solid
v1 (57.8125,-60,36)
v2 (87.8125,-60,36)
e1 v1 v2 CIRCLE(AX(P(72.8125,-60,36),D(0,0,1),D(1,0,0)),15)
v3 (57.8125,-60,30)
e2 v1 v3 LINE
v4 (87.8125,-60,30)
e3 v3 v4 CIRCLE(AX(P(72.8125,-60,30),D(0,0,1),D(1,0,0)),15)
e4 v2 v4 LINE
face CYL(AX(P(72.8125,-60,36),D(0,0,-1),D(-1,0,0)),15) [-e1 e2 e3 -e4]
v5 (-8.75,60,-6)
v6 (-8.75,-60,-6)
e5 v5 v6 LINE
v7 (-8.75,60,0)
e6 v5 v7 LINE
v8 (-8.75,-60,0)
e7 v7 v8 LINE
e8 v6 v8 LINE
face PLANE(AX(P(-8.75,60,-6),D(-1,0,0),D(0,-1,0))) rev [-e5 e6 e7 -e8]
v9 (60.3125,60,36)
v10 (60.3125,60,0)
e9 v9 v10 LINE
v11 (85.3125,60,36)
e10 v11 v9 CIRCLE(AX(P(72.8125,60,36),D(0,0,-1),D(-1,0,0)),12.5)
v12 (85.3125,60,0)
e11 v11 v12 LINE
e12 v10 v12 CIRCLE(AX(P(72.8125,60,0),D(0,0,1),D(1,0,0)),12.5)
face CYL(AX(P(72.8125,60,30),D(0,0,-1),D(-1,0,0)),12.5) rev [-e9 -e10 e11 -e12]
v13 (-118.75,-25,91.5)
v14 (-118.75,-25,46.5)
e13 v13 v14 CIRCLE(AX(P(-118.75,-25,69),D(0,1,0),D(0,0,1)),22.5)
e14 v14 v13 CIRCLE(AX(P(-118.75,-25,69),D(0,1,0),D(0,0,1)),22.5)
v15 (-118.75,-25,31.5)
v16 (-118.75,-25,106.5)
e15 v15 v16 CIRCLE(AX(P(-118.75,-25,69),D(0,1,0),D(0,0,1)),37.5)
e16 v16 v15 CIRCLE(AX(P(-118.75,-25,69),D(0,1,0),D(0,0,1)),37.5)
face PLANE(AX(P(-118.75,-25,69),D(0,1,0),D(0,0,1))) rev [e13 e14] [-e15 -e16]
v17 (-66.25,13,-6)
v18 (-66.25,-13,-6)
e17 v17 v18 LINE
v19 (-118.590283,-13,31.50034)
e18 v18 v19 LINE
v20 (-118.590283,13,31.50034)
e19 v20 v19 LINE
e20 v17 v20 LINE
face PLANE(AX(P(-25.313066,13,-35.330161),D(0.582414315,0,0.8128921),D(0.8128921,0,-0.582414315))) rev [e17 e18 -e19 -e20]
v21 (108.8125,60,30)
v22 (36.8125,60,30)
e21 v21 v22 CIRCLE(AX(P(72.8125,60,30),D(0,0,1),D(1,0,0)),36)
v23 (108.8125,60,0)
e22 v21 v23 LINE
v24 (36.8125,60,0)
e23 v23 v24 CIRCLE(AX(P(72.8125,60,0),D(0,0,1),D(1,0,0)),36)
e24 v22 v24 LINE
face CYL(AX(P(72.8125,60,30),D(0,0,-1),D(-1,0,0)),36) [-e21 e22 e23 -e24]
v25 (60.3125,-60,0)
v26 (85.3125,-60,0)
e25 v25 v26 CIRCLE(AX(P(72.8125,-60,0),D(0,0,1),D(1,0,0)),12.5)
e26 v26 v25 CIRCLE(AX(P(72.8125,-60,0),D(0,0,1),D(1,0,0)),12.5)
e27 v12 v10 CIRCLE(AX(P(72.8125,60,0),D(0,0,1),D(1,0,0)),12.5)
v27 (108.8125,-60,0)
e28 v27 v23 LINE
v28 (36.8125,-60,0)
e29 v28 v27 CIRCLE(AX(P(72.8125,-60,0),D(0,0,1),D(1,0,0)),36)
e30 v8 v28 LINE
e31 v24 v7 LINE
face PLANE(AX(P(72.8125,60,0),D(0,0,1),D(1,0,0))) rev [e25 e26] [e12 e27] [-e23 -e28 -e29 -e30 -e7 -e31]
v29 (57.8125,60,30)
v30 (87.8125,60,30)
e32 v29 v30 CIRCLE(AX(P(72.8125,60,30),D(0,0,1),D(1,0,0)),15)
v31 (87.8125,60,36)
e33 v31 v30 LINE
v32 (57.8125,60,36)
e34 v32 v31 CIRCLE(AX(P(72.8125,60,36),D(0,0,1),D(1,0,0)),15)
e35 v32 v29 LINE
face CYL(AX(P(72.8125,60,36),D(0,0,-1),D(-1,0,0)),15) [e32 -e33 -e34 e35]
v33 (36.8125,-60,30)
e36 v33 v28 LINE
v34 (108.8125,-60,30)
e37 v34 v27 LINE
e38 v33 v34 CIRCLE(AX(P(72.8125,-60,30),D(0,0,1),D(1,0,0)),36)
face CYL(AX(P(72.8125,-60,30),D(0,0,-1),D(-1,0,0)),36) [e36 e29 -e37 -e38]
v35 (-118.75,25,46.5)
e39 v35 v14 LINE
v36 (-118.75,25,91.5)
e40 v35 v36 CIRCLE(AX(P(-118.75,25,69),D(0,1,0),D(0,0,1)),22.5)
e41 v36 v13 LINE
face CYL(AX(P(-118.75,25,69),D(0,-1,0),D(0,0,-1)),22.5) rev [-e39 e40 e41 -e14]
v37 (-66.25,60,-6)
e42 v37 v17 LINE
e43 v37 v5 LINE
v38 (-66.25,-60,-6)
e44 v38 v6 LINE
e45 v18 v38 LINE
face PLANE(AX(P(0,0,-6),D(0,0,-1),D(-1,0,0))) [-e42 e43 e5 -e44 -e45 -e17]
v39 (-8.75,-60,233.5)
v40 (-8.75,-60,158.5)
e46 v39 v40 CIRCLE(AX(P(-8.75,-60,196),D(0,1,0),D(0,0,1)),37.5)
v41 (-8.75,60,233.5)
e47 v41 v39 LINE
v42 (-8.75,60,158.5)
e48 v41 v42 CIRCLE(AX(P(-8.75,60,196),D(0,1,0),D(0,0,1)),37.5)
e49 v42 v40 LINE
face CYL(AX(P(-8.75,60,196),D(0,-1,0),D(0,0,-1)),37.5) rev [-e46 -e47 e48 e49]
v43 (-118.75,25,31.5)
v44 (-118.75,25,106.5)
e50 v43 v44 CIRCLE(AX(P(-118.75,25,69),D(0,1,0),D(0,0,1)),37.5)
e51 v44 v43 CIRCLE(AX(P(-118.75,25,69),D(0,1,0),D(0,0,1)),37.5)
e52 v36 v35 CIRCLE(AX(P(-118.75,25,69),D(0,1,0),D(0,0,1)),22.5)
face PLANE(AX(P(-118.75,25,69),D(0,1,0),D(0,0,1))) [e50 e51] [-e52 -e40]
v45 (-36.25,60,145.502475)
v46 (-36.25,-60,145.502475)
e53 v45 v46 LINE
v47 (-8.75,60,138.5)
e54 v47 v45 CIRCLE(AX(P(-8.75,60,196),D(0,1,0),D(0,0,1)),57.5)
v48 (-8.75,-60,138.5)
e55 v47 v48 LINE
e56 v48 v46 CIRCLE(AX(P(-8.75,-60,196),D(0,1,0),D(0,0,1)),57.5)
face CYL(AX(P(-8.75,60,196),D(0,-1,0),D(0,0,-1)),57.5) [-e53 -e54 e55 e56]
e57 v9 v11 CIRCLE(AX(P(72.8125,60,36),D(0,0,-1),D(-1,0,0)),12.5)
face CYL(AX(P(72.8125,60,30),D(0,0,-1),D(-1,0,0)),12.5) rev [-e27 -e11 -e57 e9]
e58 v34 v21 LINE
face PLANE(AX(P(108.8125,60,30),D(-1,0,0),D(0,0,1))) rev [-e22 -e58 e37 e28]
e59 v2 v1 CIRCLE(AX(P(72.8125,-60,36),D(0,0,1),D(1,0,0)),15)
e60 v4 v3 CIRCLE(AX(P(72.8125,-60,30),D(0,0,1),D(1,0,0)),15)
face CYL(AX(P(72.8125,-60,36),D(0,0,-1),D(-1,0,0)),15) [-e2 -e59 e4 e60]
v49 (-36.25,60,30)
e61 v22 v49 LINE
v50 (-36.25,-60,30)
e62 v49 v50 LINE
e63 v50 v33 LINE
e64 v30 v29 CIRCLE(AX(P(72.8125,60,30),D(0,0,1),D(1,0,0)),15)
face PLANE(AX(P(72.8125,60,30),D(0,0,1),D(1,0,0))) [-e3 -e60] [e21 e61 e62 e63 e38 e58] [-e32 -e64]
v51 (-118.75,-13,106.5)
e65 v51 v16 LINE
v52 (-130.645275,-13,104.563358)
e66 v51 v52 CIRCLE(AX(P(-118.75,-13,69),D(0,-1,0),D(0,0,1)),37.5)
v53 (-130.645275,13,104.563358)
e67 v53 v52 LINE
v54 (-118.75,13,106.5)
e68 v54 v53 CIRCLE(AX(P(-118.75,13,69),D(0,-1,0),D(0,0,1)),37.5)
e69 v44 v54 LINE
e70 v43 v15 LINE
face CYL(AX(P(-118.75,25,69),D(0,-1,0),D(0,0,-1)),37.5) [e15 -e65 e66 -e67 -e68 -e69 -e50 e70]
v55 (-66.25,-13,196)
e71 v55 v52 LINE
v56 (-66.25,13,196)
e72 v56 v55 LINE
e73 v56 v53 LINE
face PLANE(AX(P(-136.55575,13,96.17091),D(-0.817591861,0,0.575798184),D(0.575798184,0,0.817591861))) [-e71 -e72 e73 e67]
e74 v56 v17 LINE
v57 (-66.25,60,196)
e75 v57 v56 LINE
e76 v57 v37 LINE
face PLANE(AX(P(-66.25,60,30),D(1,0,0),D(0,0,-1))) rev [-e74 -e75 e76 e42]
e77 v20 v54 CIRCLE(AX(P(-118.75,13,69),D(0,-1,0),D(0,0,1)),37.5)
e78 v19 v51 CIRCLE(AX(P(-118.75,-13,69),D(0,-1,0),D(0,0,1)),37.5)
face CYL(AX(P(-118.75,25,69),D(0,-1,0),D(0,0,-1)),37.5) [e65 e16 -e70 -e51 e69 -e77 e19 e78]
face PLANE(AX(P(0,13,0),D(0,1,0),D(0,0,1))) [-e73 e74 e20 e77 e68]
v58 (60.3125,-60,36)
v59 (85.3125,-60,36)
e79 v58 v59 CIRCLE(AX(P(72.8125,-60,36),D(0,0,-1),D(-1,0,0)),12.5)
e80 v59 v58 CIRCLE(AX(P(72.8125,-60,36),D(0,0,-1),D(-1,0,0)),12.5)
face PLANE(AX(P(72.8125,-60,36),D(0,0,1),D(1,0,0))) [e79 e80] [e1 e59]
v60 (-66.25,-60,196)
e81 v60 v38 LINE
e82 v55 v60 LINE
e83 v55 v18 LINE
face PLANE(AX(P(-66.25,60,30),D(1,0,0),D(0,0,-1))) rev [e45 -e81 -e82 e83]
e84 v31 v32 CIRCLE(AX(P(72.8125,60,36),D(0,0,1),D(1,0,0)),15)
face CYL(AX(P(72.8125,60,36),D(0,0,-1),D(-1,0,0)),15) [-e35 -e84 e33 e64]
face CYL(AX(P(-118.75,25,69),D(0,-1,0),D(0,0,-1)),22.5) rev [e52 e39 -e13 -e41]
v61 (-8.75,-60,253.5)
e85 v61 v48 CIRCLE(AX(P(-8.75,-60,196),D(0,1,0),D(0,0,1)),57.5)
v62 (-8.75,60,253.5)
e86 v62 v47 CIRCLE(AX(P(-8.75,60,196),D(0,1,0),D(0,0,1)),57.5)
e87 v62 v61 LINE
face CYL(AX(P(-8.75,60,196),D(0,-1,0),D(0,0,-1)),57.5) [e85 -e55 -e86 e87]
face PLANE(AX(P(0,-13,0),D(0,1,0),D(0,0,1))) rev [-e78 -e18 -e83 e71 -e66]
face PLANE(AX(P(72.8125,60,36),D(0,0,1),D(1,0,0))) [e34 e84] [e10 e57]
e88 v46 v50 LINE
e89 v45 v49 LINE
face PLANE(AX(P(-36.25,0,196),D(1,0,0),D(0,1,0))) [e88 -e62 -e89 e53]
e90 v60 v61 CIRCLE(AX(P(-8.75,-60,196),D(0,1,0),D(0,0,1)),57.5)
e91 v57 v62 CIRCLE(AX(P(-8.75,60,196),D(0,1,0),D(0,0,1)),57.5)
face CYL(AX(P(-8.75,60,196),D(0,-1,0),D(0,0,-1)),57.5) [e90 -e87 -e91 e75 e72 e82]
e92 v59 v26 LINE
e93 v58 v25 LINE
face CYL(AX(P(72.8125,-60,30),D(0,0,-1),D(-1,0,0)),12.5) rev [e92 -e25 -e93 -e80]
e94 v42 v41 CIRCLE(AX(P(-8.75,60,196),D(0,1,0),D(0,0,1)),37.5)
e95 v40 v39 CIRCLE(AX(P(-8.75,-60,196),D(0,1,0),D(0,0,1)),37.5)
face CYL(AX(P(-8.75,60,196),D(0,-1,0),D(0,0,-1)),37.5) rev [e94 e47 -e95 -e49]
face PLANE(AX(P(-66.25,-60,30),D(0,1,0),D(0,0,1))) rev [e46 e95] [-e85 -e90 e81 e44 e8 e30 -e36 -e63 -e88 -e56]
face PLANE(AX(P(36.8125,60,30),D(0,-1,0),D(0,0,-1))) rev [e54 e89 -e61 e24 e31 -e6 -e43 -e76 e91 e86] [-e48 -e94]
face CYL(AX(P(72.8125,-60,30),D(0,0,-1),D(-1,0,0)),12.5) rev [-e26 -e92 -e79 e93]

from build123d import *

# Parameters (mm, degrees)
BASE_PLATE_PROFILE_SKETCH_R = 12.5
BASE_LUG_PLATE_DEPTH        = 30
HOLE_BOSS_SKETCH_R          = 15
HOLE_BOSS_PADS_DEPTH        = 6
MOUNTING_HOLES_SKETCH_R     = 12.5
MOUNTING_HOLES_DEPTH        = 150.506388346
FLANGE_PAD_SKETCH_W         = 57.5
FLANGE_PAD_SKETCH_H         = 120
FLANGE_PAD_DEPTH            = 6
CONNECTING_ARM_SKETCH_W     = 30
CONNECTING_ARM_SKETCH_H     = 120
CONNECTING_ARM_DEPTH        = 166
VERTICAL_WEB_SKETCH_R       = 57.5
VERTICAL_WEB_SKETCH_R_2     = 37.5
VERTICAL_WEB_DEPTH          = 60
ARM_TRIM_CUT_DEPTH          = 317.920195248
HUB_NECK_DEPTH              = 13
HUB_CYLINDER_SKETCH_R       = 37.5
HUB_CYLINDER_SKETCH_R_2     = 22.5
HUB_CYLINDER_DEPTH          = 25
HUB_BORE_SKETCH_R           = 22.5
HUB_BORE_DEPTH              = 318.107730117


with BuildPart() as part:
    # Base Plate Profile Sketch → Base Lug Plate (new body)
    with BuildSketch(Plane.XY):
        with BuildLine():
            Line((108.8125, 60), (108.8125, -60))
            ThreePointArc((108.8125, -60), (72.8125, -96), (36.8125, -60))
            Line((36.8125, -60), (-66.25, -60))
            Line((-66.25, -60), (-66.25, 60))
            Line((-66.25, 60), (36.8125, 60))
            ThreePointArc((36.8125, 60), (72.8125, 96), (108.8125, 60))
        make_face()
        with Locations((72.8125, 60)):
            Circle(BASE_PLATE_PROFILE_SKETCH_R, mode=Mode.SUBTRACT)
        with Locations((72.8125, -60)):
            Circle(BASE_PLATE_PROFILE_SKETCH_R, mode=Mode.SUBTRACT)
    extrude(amount=BASE_LUG_PLATE_DEPTH)

    # Hole Boss Sketch → Hole Boss Pads (add)
    with BuildSketch(Plane.XY.offset(30)):
        with Locations((72.8125, 60)):
            Circle(HOLE_BOSS_SKETCH_R)
        with Locations((72.8125, -60)):
            Circle(HOLE_BOSS_SKETCH_R)
    extrude(amount=HOLE_BOSS_PADS_DEPTH)

    # Mounting Holes Sketch → Mounting Holes (cut, through all)
    with BuildSketch(Plane(origin=(0, 0, 0), x_dir=(-1, 0, 0), z_dir=(0, 0, -1))):
        with Locations((-72.8125, 60)):
            Circle(MOUNTING_HOLES_SKETCH_R)
        with Locations((-72.8125, -60)):
            Circle(MOUNTING_HOLES_SKETCH_R)
    extrude(amount=-MOUNTING_HOLES_DEPTH, mode=Mode.SUBTRACT)

    # Flange Pad Sketch → Flange Pad (add)
    with BuildSketch(Plane(origin=(0, 0, 0), x_dir=(-1, 0, 0), z_dir=(0, 0, -1))):
        with Locations((37.5, 0)):
            Rectangle(FLANGE_PAD_SKETCH_W, FLANGE_PAD_SKETCH_H)
    extrude(amount=FLANGE_PAD_DEPTH)

    # Connecting Arm Sketch → Connecting Arm (add)
    with BuildSketch(Plane.XY.offset(30)):
        with Locations((-51.25, 0)):
            Rectangle(CONNECTING_ARM_SKETCH_W, CONNECTING_ARM_SKETCH_H)
    extrude(amount=CONNECTING_ARM_DEPTH)

    # Vertical Web Sketch → Vertical Web (add, symmetric)
    with BuildSketch(Plane(origin=(0, 0, 0), x_dir=(1, 0, 0), z_dir=(0, 1, 0))):
        with Locations((-8.75, -196)):
            Circle(VERTICAL_WEB_SKETCH_R)
        with Locations((-8.75, -196)):
            Circle(VERTICAL_WEB_SKETCH_R_2, mode=Mode.SUBTRACT)
    extrude(amount=VERTICAL_WEB_DEPTH, both=True)

    # Arm Trim Sketch → Arm Trim Cut (cut, through all)
    with BuildSketch(Plane(origin=(0, 60, 0), x_dir=(1, 0, 0), z_dir=(0, 1, 0))):
        with BuildLine():
            Line((-36.25, -196), (-36.25, -170.504902432))
            ThreePointArc((-36.25, -170.504902432), (-43.660600109, -182.306936062), (-46.25, -196))
            Line((-46.25, -196), (-36.25, -196))
        make_face()
    extrude(amount=-ARM_TRIM_CUT_DEPTH, mode=Mode.SUBTRACT)

    # Hub Neck Sketch → Hub Neck (add, symmetric)
    with BuildSketch(Plane(origin=(0, 0, 0), x_dir=(1, 0, 0), z_dir=(0, 1, 0))):
        with BuildLine():
            Line((-141.503483954, -89.145484499), (-66.25, -196))
            Line((-66.25, -196), (-66.25, 6))
            Line((-66.25, 6), (-136.449661852, -44.296082333))
            ThreePointArc((-136.449661852, -44.296082333), (-148.385562866, -62.269844624), (-145.38363754, -83.635946473))
            Line((-145.38363754, -83.635946473), (-141.503483954, -89.145484499))
        make_face()
    extrude(amount=HUB_NECK_DEPTH, both=True)

    # Hub Cylinder Sketch → Hub Cylinder (add, symmetric)
    with BuildSketch(Plane(origin=(0, 0, 0), x_dir=(1, 0, 0), z_dir=(0, 1, 0))):
        with Locations(Location((-118.75, -69, 0), (0, 0, 270))):
            Circle(HUB_CYLINDER_SKETCH_R)
        with Locations(Location((-118.75, -69, 0), (0, 0, 270))):
            Circle(HUB_CYLINDER_SKETCH_R_2, mode=Mode.SUBTRACT)
    extrude(amount=HUB_CYLINDER_DEPTH, both=True)

    # Hub Bore Sketch → Hub Bore (cut, through all)
    with BuildSketch(Plane(origin=(0, 13, 0), x_dir=(1, 0, 0), z_dir=(0, 1, 0))):
        with Locations(Location((-118.75, -69, 0), (0, 0, 270))):
            Circle(HUB_BORE_SKETCH_R)
    extrude(amount=-HUB_BORE_DEPTH, mode=Mode.SUBTRACT)


solid = part.part
